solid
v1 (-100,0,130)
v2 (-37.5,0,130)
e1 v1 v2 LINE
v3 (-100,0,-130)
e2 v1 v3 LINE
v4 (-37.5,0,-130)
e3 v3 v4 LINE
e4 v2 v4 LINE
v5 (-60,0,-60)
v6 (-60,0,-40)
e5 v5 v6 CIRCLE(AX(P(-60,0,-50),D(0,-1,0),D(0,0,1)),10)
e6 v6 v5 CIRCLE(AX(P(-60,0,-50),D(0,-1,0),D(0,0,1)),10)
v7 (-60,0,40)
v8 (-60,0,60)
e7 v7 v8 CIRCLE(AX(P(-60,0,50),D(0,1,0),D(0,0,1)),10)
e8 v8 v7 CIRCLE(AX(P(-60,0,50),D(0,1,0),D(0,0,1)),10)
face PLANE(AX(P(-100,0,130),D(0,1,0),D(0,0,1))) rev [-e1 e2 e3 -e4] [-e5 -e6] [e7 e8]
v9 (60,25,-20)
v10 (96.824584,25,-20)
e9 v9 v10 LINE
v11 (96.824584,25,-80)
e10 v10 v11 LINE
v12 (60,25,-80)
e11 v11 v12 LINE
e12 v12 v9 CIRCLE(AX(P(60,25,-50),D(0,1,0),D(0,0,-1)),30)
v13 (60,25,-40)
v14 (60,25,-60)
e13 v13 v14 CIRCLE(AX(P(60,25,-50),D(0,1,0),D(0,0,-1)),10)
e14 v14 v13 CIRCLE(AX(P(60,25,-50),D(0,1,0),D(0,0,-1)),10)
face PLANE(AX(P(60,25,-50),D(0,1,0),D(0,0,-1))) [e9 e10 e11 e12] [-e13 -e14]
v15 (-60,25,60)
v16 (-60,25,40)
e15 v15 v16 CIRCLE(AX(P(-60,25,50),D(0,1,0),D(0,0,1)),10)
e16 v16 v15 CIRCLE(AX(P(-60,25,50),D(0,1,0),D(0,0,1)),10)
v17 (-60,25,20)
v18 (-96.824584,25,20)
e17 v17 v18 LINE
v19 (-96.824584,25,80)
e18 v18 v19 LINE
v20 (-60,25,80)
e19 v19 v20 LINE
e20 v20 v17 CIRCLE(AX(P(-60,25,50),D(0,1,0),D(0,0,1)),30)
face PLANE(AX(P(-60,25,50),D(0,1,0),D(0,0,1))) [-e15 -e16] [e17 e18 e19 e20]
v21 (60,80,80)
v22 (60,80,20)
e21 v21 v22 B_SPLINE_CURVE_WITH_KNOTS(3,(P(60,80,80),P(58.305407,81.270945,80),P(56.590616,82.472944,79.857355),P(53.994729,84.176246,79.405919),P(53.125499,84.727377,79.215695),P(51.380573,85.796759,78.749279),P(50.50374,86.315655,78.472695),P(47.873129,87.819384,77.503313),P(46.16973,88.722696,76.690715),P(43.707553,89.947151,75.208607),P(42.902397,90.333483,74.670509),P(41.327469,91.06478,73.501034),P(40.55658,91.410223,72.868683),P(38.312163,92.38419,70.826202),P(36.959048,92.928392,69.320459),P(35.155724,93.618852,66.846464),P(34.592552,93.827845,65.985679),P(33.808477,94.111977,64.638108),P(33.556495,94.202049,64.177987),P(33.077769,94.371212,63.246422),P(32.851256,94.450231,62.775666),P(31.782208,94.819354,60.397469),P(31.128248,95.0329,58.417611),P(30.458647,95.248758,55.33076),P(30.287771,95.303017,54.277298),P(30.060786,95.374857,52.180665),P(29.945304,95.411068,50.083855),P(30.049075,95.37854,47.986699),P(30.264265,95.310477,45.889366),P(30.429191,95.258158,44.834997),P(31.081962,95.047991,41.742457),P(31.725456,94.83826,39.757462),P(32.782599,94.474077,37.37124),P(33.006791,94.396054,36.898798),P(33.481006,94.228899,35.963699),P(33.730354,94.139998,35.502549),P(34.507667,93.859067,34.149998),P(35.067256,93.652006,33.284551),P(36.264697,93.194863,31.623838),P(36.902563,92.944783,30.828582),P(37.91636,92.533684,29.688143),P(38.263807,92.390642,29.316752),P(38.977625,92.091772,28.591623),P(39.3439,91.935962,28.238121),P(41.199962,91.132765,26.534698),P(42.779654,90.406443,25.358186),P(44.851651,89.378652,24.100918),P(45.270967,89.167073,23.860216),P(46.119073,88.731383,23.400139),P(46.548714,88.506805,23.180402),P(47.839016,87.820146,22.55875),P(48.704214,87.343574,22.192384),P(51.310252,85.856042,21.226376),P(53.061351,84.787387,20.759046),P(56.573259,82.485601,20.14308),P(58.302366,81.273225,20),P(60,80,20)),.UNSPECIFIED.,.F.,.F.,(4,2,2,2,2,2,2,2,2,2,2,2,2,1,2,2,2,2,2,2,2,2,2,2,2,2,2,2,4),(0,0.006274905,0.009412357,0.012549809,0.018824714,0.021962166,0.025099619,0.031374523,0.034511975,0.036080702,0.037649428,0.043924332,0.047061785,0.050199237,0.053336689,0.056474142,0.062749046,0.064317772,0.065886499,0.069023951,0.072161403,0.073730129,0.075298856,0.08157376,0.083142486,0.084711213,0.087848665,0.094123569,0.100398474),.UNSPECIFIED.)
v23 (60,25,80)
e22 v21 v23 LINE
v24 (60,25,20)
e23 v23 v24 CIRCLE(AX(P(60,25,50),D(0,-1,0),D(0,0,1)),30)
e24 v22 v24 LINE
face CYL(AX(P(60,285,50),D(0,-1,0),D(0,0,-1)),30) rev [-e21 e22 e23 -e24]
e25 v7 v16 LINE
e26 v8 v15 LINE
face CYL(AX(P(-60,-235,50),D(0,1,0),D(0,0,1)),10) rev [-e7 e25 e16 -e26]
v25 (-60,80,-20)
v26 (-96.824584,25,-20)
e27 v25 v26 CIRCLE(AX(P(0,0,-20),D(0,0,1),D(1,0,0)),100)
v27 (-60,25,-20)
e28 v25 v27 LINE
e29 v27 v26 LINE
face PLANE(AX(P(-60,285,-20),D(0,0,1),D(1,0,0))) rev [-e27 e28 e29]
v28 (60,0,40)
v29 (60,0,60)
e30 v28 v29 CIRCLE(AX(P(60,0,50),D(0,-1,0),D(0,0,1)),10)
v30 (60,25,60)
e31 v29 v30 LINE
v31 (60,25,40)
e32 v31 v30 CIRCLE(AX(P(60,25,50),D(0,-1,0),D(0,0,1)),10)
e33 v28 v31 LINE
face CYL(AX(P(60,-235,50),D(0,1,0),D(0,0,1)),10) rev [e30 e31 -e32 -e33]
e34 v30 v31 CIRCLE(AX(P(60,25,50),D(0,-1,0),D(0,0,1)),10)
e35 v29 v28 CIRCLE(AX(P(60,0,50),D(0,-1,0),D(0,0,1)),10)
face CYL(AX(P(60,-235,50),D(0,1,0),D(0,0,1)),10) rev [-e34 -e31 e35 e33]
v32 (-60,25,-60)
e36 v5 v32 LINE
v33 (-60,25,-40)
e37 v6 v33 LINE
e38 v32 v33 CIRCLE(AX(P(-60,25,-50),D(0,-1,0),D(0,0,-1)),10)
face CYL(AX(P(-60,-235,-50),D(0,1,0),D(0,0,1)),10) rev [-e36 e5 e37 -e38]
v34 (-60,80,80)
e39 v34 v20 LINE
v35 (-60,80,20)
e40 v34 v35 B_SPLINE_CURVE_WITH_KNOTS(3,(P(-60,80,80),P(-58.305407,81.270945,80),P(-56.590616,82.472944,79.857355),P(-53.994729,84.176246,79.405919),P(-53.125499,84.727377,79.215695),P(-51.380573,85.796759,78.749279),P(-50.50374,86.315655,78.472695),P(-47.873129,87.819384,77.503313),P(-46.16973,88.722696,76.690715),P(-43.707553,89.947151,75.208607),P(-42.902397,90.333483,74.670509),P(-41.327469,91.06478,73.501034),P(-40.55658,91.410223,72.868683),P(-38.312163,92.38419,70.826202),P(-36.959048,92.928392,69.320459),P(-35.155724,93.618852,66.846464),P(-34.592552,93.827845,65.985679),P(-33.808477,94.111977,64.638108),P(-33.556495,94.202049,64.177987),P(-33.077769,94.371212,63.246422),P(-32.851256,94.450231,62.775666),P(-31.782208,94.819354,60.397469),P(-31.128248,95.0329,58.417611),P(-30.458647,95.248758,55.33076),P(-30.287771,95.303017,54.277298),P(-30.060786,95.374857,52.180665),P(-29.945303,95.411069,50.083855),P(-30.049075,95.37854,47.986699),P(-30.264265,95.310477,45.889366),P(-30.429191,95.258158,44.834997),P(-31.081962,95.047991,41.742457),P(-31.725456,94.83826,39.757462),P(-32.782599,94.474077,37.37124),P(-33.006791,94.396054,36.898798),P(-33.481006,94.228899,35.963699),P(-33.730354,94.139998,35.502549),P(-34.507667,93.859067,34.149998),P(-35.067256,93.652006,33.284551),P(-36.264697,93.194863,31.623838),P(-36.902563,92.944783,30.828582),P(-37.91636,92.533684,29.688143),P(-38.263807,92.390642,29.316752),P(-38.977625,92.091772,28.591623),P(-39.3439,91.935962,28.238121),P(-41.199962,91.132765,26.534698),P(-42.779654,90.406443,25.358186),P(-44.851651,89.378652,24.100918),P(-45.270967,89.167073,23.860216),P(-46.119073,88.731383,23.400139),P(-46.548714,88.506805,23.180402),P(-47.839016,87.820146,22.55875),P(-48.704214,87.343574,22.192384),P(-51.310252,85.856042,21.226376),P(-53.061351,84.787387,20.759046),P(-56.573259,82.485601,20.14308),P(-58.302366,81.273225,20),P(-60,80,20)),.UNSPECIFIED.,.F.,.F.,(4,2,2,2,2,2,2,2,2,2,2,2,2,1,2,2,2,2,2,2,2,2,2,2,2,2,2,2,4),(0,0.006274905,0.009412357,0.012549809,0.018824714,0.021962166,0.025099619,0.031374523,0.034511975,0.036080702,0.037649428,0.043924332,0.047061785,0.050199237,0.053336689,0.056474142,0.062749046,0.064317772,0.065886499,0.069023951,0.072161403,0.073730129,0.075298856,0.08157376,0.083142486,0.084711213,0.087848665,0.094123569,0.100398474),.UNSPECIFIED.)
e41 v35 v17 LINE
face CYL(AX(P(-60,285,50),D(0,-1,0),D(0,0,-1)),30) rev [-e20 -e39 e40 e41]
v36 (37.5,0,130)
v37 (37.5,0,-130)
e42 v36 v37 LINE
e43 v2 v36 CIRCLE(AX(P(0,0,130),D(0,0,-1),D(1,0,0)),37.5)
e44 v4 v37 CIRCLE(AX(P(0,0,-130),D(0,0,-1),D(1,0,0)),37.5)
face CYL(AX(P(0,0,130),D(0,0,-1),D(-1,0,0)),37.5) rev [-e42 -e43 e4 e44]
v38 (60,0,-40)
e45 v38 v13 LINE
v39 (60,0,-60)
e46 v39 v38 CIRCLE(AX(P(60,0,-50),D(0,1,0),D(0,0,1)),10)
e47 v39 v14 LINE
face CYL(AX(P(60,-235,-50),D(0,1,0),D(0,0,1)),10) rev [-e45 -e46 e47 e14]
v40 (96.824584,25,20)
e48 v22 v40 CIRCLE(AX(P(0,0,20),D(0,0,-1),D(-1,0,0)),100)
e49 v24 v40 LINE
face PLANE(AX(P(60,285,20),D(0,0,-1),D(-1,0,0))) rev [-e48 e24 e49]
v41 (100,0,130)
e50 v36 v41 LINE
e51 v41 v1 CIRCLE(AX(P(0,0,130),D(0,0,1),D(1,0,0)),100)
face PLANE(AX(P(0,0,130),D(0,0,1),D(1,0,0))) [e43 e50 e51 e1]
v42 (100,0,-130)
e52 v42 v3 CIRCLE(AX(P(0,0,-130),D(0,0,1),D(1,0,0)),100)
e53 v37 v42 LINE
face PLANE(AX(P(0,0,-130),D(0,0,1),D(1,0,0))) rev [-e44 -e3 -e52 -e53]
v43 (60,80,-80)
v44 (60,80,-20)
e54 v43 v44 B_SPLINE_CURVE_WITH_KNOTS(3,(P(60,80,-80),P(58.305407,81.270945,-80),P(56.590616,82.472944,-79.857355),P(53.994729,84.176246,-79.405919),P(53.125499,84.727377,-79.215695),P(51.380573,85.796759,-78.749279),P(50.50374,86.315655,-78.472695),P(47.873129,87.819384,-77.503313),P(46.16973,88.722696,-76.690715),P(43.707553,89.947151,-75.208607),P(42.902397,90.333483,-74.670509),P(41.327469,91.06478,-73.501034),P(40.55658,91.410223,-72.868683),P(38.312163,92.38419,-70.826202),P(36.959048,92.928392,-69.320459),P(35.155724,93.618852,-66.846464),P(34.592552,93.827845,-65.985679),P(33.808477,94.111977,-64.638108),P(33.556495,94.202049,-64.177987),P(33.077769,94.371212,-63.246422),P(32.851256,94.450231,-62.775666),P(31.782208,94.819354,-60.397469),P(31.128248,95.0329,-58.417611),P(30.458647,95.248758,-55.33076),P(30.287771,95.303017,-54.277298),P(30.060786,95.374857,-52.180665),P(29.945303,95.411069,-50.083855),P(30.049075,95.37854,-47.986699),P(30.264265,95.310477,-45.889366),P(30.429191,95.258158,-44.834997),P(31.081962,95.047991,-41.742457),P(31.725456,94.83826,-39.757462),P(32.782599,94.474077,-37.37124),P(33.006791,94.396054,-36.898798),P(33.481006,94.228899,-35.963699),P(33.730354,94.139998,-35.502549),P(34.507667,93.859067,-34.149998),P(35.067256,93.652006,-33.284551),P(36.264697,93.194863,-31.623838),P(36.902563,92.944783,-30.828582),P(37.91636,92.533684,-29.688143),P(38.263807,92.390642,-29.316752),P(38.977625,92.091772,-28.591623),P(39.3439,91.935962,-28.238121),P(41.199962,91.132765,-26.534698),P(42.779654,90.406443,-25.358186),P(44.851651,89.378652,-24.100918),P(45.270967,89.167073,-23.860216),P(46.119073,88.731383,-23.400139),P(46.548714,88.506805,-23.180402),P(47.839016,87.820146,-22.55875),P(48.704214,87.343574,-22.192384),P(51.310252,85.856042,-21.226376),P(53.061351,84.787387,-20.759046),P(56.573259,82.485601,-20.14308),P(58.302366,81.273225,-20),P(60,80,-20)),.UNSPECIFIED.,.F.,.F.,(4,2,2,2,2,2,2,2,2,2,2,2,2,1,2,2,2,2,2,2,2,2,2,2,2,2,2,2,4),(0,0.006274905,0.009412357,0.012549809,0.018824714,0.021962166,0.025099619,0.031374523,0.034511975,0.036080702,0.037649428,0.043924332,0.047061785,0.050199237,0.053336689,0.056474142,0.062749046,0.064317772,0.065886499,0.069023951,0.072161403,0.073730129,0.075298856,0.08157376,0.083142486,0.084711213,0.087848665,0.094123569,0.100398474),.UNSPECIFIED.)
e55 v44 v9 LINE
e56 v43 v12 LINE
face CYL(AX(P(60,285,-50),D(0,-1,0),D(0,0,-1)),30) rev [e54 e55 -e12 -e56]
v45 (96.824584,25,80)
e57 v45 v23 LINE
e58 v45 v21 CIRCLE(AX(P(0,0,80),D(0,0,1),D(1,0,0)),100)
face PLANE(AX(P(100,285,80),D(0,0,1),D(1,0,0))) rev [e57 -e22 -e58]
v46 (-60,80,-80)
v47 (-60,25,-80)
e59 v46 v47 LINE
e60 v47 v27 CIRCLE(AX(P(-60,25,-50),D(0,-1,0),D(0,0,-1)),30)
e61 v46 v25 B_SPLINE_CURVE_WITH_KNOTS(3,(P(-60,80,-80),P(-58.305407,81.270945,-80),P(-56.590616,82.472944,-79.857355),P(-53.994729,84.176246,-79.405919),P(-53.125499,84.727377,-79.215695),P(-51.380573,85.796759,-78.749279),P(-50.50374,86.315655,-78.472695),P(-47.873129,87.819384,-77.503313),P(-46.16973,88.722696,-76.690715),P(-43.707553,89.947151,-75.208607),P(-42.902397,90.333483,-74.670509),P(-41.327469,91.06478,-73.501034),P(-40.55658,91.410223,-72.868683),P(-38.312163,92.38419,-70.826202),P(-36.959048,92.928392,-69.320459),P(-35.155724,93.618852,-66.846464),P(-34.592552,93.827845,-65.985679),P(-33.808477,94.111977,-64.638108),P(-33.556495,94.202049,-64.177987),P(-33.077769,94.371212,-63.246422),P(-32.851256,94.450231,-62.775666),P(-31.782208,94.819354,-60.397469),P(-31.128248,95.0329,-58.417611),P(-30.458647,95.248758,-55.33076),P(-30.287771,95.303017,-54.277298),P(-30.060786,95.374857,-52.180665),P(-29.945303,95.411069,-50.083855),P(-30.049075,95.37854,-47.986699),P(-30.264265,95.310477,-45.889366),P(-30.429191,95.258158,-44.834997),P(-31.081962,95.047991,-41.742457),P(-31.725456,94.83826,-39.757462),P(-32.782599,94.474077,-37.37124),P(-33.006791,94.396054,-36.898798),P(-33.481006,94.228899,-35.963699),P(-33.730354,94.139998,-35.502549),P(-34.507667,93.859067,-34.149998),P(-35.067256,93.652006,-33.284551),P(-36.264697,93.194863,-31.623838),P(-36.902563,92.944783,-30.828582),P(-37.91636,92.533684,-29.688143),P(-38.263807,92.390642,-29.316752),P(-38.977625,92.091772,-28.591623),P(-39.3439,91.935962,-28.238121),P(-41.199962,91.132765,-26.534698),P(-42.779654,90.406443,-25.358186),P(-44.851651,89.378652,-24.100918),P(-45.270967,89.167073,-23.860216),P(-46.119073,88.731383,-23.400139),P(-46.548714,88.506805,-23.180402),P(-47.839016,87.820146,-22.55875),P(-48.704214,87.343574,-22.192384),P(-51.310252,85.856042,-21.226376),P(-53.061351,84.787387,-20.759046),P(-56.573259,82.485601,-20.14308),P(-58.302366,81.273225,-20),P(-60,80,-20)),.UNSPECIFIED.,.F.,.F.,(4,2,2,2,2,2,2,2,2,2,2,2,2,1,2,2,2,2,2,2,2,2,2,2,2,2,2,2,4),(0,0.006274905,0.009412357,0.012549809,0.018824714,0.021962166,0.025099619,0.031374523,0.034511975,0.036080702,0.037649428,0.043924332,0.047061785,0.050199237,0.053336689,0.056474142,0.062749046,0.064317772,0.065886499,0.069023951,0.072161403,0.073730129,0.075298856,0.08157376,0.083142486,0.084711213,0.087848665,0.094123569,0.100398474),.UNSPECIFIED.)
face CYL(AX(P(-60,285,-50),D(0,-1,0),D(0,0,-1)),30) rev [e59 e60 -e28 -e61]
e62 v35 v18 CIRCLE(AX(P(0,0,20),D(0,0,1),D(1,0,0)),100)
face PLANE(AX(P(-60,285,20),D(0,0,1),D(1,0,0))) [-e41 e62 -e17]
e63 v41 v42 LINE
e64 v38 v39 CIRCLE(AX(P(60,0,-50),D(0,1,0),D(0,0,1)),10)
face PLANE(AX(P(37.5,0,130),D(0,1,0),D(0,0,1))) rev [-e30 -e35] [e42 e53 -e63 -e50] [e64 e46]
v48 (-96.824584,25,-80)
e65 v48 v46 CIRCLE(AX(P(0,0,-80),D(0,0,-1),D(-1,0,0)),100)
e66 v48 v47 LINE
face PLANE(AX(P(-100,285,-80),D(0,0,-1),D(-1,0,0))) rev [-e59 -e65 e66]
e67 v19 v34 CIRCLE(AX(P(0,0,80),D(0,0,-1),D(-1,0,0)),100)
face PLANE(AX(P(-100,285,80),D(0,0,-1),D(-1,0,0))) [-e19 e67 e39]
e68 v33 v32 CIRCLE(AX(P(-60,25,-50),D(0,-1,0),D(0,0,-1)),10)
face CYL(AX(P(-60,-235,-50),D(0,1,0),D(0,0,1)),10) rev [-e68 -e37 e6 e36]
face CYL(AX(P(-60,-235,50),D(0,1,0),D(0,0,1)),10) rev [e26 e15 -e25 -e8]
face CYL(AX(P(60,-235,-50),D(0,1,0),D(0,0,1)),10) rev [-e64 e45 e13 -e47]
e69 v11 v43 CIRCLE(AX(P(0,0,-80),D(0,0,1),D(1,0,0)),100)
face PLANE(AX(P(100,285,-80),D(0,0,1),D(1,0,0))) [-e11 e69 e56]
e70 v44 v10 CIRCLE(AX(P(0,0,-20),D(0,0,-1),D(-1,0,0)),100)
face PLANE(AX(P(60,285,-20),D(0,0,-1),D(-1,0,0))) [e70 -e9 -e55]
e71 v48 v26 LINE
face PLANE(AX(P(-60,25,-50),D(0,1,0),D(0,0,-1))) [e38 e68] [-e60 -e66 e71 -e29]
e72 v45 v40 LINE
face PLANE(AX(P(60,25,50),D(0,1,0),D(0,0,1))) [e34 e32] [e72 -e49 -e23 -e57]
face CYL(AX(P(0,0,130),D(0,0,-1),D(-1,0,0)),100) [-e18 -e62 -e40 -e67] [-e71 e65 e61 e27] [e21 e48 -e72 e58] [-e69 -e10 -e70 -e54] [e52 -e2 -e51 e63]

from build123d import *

# Parameters (mm, degrees)
BLOCK_BODY_260_DEPTH                   = 130
BOLT_START                             = 25
BOLT_POCKET_60X80_DEPTH                = 260
BOLT_POCKET_MIRROR_RIGHT_COPY_1_DEPTH  = 260
BOLT_HOLE_SKETCH_R                     = 10
BOLT_HOLE_CUT_DEPTH                    = 260
BOLT_HOLE_MIRROR_RIGHT_COPY_1_SKETCH_R = 10
BOLT_HOLE_MIRROR_RIGHT_COPY_1_DEPTH    = 260


with BuildPart() as part:
    # Block Profile Sketch → Block Body 260 (new, symmetric)
    with BuildSketch(Plane.XY):
        with BuildLine():
            Line((-100, 0), (-37.5, 0))
            ThreePointArc((-37.5, 0), (0, 37.5), (37.5, 0))
            Line((37.5, 0), (100, 0))
            ThreePointArc((100, 0), (0, 100), (-100, 0))
        make_face()
    extrude(amount=BLOCK_BODY_260_DEPTH, both=True)

    # Bolt Pocket Sketch → Bolt Pocket 60x80 (cut)
    with BuildSketch(Plane(origin=(0, 0, 0), x_dir=(1, 0, 0), z_dir=(0, 1, 0)).offset(BOLT_START)):
        with BuildLine():
            Line((-60, -20), (-100, -20))
            Line((-100, -20), (-100, -80))
            Line((-100, -80), (-60, -80))
            ThreePointArc((-60, -80), (-30, -50), (-60, -20))
        make_face()
    bolt_pocket_60x80 = extrude(amount=BOLT_POCKET_60X80_DEPTH, mode=Mode.SUBTRACT)

    # Bolt Pocket Mirror Front: Bolt Pocket 60x80 across plane
    add(bolt_pocket_60x80.mirror(Plane.XY), mode=Mode.SUBTRACT)

    # Bolt Pocket Mirror Right: Bolt Pocket 60x80 across plane
    add(bolt_pocket_60x80.mirror(Plane(origin=(0, 0, 0), x_dir=(0, 0, 1), z_dir=(1, 0, 0))), mode=Mode.SUBTRACT)

    # Bolt Pocket Mirror Right copy 1 sketch → Bolt Pocket Mirror Right copy 1 (cut)
    with BuildSketch(Plane(origin=(0, 0, 0), x_dir=(-1, 0, 0), z_dir=(0, 1, 0)).offset(BOLT_START)):
        with BuildLine():
            Line((-60, -20), (-100, -20))
            Line((-100, -20), (-100, -80))
            Line((-100, -80), (-60, -80))
            ThreePointArc((-60, -80), (-30, -50), (-60, -20))
        make_face()
    extrude(amount=BOLT_POCKET_MIRROR_RIGHT_COPY_1_DEPTH, mode=Mode.SUBTRACT)

    # Bolt Hole Sketch → Bolt Hole Cut (cut)
    with BuildSketch(Plane(origin=(0, 25, 0), x_dir=(1, 0, 0), z_dir=(0, 1, 0))):
        with Locations(Location((-60, -50, 0), (0, 0, 270))):
            Circle(BOLT_HOLE_SKETCH_R)
    bolt_hole_cut = extrude(amount=-BOLT_HOLE_CUT_DEPTH, mode=Mode.SUBTRACT)

    # Bolt Hole Mirror Front: Bolt Hole Cut across plane
    add(bolt_hole_cut.mirror(Plane.XY), mode=Mode.SUBTRACT)

    # Bolt Hole Mirror Right: Bolt Hole Cut across plane
    add(bolt_hole_cut.mirror(Plane(origin=(0, 0, 0), x_dir=(0, 0, 1), z_dir=(1, 0, 0))), mode=Mode.SUBTRACT)

    # Bolt Hole Mirror Right copy 1 sketch → Bolt Hole Mirror Right copy 1 (cut)
    with BuildSketch(Plane(origin=(0, 25, 0), x_dir=(-1, 0, 0), z_dir=(0, 1, 0))):
        with Locations(Location((-60, -50, 0), (0, 0, 270))):
            Circle(BOLT_HOLE_MIRROR_RIGHT_COPY_1_SKETCH_R)
    extrude(amount=-BOLT_HOLE_MIRROR_RIGHT_COPY_1_DEPTH, mode=Mode.SUBTRACT)


solid = part.part
